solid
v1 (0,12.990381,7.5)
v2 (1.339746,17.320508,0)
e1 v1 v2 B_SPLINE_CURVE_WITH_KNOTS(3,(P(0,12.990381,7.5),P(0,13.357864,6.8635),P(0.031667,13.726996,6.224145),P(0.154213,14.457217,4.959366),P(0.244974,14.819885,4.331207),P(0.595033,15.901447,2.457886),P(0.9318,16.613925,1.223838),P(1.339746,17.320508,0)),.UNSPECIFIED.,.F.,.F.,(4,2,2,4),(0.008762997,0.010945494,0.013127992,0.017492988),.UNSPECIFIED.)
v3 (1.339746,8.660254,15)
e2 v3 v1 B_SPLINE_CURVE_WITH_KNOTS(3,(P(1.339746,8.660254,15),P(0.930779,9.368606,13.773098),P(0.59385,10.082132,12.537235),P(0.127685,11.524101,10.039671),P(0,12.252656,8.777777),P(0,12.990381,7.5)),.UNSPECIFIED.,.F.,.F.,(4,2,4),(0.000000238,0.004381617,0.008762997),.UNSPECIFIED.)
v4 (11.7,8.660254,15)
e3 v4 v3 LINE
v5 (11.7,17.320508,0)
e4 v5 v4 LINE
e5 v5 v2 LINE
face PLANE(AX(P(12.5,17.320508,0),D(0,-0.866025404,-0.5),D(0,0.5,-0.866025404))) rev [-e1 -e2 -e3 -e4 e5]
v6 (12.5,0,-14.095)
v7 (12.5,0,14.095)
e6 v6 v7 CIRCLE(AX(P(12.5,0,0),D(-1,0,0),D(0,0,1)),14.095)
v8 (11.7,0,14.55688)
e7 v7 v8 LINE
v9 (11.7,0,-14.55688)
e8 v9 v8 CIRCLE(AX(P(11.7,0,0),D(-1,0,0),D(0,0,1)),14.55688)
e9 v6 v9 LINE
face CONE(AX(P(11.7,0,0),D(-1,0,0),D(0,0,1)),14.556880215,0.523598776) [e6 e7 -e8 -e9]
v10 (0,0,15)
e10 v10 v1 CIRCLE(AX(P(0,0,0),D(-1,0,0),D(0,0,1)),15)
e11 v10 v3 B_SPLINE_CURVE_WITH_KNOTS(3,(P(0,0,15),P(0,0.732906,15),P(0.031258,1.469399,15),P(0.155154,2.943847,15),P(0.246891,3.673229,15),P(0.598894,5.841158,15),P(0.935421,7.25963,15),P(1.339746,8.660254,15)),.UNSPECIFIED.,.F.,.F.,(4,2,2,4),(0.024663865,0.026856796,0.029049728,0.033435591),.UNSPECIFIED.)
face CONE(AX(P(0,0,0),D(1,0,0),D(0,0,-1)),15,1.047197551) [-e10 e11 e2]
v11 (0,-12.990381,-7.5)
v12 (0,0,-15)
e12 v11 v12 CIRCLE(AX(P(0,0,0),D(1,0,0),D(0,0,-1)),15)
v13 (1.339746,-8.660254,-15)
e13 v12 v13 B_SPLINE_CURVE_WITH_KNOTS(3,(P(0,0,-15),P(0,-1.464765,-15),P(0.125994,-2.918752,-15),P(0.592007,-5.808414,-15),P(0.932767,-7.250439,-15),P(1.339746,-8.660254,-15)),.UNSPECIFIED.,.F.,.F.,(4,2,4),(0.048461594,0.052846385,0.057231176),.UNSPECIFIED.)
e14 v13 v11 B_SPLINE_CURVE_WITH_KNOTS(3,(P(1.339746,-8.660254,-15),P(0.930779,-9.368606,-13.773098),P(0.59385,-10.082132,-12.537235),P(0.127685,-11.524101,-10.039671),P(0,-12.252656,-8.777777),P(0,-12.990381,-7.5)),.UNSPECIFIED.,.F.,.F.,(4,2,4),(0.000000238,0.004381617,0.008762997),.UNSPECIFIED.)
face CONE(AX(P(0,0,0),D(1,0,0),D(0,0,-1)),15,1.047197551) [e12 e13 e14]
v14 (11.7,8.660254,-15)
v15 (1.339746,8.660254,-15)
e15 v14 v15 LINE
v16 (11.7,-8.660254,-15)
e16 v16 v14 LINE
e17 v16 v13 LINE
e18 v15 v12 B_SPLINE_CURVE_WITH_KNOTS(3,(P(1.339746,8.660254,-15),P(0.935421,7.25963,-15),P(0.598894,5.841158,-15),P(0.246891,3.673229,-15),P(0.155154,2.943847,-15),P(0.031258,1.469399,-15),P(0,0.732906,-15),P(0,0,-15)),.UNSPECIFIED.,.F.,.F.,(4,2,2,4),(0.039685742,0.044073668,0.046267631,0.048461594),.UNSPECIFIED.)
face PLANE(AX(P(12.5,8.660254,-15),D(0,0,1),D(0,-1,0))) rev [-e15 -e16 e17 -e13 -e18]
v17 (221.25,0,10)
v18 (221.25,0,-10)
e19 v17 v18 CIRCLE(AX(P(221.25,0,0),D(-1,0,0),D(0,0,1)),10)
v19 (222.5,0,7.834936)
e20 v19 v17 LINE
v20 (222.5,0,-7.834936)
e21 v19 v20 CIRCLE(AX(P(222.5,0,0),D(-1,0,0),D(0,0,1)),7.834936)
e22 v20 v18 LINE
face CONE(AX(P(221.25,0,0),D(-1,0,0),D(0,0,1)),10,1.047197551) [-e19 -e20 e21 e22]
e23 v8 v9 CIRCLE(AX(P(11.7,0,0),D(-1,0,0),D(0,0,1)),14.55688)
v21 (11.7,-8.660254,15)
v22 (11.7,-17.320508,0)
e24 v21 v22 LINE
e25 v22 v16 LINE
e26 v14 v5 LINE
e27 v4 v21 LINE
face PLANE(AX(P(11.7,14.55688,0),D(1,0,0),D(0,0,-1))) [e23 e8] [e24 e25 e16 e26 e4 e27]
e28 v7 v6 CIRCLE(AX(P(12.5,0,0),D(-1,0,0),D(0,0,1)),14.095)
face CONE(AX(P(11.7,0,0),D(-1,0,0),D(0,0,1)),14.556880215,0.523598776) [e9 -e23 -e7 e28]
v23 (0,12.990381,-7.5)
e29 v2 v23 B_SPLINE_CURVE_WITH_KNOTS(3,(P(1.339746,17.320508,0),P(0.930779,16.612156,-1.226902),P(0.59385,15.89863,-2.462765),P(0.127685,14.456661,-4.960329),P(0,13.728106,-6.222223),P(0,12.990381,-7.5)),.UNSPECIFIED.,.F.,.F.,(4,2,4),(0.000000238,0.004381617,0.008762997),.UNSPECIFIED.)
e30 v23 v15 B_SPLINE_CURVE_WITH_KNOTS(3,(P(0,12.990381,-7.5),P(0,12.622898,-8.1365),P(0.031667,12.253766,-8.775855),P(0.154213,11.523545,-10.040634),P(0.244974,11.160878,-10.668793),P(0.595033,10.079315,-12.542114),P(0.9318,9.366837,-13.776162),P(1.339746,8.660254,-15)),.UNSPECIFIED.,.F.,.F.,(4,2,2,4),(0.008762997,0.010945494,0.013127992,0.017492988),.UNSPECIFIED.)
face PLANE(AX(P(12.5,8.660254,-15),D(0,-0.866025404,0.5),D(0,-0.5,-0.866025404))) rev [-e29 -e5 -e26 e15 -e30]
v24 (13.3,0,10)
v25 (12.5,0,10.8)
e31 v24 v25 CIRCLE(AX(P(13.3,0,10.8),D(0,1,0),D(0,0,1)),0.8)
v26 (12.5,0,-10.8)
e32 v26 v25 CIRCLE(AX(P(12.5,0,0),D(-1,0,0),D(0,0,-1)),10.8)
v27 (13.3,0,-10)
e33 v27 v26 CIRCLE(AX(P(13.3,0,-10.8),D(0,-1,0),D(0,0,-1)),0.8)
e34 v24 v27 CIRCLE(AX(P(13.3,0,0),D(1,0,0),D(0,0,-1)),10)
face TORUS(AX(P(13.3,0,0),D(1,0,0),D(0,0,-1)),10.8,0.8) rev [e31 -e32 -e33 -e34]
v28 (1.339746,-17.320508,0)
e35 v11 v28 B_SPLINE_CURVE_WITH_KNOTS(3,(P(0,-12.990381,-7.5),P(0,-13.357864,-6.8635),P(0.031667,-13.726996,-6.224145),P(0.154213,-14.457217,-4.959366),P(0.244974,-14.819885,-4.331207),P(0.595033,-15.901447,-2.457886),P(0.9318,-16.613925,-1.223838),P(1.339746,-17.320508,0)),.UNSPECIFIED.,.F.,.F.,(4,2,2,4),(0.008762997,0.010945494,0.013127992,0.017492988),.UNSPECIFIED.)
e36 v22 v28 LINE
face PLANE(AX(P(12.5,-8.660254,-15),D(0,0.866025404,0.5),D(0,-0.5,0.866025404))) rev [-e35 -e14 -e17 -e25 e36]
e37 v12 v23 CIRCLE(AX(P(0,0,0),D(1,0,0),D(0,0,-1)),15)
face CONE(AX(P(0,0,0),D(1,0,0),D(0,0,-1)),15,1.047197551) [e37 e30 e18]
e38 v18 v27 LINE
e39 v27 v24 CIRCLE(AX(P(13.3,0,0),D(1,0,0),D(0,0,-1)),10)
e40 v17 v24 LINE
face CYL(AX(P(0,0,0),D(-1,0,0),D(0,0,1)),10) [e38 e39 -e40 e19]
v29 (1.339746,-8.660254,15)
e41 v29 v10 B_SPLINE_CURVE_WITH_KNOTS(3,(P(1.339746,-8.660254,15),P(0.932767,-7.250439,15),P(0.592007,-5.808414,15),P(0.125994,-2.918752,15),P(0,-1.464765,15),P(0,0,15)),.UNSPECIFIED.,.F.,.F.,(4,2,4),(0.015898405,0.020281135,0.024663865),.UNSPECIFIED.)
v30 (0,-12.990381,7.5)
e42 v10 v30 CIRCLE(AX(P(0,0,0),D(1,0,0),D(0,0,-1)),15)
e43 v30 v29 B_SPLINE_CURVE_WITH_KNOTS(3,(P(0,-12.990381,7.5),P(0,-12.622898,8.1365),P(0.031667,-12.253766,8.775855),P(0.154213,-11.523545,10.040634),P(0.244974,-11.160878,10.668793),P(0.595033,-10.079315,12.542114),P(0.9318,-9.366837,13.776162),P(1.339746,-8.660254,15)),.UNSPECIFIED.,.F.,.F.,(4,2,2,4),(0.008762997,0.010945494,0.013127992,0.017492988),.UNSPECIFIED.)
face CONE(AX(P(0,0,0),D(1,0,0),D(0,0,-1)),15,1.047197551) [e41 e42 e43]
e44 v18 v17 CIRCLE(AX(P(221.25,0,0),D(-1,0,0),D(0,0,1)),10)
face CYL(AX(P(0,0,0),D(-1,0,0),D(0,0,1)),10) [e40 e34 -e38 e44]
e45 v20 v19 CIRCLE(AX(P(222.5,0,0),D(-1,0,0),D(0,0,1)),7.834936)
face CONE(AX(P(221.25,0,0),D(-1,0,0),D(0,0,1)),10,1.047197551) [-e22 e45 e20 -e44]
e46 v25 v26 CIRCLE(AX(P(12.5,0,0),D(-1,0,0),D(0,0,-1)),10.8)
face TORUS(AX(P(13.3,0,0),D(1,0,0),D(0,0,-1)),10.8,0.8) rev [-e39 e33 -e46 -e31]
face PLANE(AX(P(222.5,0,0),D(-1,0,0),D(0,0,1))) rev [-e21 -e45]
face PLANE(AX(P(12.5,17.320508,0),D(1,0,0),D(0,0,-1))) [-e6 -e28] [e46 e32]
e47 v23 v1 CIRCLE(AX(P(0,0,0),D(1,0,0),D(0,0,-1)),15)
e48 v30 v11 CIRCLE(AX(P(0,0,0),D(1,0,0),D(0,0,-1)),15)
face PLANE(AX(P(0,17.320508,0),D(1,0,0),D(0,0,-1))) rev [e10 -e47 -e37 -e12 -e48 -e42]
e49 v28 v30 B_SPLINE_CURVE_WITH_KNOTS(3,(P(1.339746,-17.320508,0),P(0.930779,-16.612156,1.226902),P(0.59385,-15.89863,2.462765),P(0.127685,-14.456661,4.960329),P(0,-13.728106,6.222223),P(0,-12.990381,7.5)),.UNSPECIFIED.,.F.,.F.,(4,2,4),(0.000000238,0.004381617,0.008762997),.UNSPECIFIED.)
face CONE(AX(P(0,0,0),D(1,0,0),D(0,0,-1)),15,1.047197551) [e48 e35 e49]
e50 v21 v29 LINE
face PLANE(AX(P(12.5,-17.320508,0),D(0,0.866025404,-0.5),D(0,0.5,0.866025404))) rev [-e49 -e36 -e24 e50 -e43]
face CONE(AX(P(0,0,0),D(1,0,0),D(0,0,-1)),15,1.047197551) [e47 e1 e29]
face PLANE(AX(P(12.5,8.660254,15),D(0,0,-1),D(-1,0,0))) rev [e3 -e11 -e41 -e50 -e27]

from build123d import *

# Parameters (mm, degrees)
EXTRUDE_390_DEPTH = 12.5
FILLET_1319_R     = 0.8


with BuildPart() as part:
    # 草图1 → Extrude 390 (new body)
    with BuildSketch(Plane(origin=(0, 0, 0), x_dir=(0, 0, -1), z_dir=(1, 0, 0))):
        Polygon((15, 8.660254038), (15, -8.660254038), (0, -17.320508076), (-15, -8.660254038), (-15, 8.660254038), (0, 17.320508076), align=None)
    extrude(amount=EXTRUDE_390_DEPTH)

    # 草图2 → 凸台-旋转1 (revolve)
    with BuildSketch(Plane.XY, mode=Mode.PRIVATE) as revolve_1_sk:
        Polygon((0, 0), (222.5, 0), (222.5, 7.835), (222.5, 10), (170.5, 10), (0, 10), align=None)
    revolve(revolve_1_sk.sketch.rotate(Axis((0, 0, 0), (1, 0, 0)), 90), axis=Axis((0, 0, 0), (1, 0, 0)))

    # 草图3 → 切除-旋转1 (revolve, cut)
    with BuildSketch(Plane.XY):
        Polygon((0, 15), (4.226497308, 22.320508076), (4.226497308, 27.320508076), (-10, 27.320508076), (-10, 15), align=None)
    revolve(axis=Axis((0, 0, 0), (1, 0, 0)), mode=Mode.SUBTRACT)

    # 草图4 → 切除-旋转3 (revolve, cut)
    with BuildSketch(Plane.XY, mode=Mode.PRIVATE) as cut_revolve_3_sk:
        Polygon((12.5, 14.095), (11.7, 14.556880215), (11.7, 17.320508076), (12.5, 17.320508076), align=None)
    revolve(cut_revolve_3_sk.sketch.rotate(Axis((0, 0, 0), (1, 0, 0)), 90), axis=Axis((0, 0, 0), (1, 0, 0)), mode=Mode.SUBTRACT)

    # Fillet 1319
    fillet_1319_edges = [part.edges().sort_by_distance(p)[0] for p in [
        (12.5, 0, -10),
    ]]
    fillet(fillet_1319_edges, radius=FILLET_1319_R)

    # 草图6 → 切除-旋转4 (revolve, cut)
    with BuildSketch(Plane.XY, mode=Mode.PRIVATE) as cut_revolve_4_sk:
        Polygon((221.25, 10), (223.75, 10), (222.5, 7.834936491), align=None)
    revolve(cut_revolve_4_sk.sketch.rotate(Axis((0, 0, 0), (1, 0, 0)), 90), axis=Axis((0, 0, 0), (1, 0, 0)), mode=Mode.SUBTRACT)


solid = part.part
